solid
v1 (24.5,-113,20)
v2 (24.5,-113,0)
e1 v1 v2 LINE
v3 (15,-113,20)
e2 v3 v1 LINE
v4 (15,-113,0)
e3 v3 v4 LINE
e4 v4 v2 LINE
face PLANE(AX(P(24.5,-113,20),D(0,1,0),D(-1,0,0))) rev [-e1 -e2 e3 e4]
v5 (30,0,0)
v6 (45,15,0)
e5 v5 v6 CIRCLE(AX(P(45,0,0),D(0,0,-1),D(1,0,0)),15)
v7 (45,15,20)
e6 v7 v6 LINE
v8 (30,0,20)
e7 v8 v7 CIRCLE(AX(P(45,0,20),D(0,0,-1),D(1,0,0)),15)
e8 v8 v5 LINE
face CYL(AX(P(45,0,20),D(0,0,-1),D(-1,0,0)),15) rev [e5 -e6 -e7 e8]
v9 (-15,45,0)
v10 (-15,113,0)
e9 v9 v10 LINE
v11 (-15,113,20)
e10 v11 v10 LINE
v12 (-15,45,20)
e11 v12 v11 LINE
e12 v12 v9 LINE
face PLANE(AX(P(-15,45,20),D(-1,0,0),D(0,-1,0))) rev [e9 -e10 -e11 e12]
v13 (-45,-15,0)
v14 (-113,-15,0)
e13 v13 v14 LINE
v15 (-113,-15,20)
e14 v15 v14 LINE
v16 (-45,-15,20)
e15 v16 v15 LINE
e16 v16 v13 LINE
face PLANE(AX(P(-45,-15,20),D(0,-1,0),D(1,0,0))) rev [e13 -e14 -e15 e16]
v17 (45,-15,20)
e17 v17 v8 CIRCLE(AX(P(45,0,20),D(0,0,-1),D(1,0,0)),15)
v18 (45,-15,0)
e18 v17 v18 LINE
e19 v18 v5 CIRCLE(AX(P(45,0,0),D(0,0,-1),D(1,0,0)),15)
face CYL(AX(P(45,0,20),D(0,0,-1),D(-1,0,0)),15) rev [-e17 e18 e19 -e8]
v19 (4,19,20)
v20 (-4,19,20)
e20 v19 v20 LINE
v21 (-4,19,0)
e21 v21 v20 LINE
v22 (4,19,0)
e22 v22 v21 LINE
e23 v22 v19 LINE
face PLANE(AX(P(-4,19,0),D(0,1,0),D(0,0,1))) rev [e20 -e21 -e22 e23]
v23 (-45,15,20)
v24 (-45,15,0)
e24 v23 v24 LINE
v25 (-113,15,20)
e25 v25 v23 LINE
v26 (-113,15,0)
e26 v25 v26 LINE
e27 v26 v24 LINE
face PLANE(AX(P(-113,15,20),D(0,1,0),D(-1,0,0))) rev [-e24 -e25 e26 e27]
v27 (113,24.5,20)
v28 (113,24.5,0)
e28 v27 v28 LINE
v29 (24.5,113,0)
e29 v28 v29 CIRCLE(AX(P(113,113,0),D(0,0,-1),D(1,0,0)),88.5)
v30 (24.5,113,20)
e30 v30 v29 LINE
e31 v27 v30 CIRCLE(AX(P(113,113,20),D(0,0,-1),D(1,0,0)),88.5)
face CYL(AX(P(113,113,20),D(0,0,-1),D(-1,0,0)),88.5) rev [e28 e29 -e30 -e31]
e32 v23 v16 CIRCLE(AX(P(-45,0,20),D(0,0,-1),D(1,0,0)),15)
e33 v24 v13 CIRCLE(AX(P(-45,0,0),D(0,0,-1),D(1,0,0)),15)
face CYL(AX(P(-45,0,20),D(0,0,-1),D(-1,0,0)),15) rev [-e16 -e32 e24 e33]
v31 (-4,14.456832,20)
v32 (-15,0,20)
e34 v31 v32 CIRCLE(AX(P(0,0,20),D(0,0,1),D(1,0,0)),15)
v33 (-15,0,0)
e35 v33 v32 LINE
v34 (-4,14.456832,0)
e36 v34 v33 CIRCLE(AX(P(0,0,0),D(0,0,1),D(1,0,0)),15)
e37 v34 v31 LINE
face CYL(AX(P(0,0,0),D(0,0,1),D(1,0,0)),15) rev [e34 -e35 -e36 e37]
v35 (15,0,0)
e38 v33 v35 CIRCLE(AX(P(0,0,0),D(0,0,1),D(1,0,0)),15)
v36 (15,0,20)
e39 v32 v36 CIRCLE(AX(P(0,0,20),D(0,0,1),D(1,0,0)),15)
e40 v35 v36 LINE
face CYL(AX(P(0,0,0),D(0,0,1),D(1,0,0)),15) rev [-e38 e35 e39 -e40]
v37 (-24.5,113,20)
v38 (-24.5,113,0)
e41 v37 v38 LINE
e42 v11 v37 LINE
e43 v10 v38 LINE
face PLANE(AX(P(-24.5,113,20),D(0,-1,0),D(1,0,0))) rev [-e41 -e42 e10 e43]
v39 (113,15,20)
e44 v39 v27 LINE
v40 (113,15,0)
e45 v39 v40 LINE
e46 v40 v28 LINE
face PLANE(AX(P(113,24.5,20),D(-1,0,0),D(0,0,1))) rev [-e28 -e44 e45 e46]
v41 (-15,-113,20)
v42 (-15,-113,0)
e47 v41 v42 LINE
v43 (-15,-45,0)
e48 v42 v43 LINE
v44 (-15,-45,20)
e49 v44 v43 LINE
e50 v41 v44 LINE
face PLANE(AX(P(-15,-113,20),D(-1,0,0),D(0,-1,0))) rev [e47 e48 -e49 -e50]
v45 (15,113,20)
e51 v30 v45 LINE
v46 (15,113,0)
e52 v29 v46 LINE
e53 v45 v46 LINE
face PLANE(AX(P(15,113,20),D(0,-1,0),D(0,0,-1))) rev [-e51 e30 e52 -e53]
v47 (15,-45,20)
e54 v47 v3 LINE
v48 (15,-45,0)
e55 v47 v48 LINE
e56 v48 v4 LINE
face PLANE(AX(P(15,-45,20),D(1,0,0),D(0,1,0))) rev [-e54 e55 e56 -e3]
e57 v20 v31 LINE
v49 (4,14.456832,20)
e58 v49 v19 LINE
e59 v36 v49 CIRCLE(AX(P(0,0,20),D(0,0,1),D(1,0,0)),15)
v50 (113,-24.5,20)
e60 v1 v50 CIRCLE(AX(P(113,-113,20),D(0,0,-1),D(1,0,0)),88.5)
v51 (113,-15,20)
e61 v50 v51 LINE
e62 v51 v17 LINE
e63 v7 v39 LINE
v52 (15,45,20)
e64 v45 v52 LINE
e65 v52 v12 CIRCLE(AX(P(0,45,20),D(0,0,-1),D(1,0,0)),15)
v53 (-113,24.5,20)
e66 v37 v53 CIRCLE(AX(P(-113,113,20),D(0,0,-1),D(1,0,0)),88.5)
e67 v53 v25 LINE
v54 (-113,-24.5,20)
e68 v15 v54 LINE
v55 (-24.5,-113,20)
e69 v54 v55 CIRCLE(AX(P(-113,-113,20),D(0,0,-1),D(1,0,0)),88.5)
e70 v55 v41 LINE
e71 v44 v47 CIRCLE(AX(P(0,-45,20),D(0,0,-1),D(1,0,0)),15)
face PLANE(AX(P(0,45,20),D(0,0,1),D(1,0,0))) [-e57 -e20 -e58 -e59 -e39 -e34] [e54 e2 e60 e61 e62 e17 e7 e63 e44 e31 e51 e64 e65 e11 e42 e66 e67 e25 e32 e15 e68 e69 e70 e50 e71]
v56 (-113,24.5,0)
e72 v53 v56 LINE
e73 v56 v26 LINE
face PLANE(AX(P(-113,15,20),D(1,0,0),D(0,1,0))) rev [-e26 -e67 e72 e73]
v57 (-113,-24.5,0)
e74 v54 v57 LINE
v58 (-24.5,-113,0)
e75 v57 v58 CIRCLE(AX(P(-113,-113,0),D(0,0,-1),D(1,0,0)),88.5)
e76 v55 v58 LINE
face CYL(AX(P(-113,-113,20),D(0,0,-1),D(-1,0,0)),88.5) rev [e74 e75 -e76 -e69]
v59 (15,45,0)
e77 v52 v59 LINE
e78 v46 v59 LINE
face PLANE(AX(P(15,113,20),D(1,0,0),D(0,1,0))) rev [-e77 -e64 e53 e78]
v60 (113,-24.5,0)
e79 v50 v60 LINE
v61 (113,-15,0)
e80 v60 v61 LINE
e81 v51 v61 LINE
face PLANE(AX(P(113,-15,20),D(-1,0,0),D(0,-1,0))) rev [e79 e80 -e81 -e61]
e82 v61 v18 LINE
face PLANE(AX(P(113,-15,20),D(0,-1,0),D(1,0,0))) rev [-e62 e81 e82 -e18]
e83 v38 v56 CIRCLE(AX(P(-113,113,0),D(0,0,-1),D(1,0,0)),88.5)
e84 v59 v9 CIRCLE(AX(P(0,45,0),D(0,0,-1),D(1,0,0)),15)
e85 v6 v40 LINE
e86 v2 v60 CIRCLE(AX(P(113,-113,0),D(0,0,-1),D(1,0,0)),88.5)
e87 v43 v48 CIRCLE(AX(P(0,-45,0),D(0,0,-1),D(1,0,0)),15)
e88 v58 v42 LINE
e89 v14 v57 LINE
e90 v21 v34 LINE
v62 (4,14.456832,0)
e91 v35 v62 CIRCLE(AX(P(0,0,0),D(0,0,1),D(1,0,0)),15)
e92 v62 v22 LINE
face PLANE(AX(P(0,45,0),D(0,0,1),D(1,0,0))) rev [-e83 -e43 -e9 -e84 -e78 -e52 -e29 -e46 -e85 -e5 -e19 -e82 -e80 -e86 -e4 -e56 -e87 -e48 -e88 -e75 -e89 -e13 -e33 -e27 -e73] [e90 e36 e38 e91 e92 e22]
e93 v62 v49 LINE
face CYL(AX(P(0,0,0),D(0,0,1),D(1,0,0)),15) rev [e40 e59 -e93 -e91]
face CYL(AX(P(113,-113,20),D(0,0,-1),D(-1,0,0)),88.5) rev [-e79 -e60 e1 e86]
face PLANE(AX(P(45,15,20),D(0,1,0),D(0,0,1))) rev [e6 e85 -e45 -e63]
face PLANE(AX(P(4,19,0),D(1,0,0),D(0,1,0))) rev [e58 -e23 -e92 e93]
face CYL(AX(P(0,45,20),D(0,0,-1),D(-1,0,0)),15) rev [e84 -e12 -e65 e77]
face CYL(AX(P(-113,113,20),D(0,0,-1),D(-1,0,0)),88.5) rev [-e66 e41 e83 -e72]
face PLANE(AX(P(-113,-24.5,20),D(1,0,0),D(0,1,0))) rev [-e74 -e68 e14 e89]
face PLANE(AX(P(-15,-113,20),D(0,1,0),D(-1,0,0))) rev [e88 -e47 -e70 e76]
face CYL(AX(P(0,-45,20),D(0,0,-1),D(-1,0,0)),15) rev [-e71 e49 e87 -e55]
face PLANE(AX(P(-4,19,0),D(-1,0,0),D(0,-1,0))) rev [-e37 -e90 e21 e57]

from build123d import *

# Parameters (mm, degrees)
EXTRUDE_1_DEPTH     = 20
CUT_EXTRUDE_1_DEPTH = 162.052786378


with BuildPart() as part:
    # 草图1 → 凸台-拉伸1 (new body)
    with BuildSketch(Plane.XY):
        with BuildLine():
            Line((45, 15), (113, 15))
            Line((113, 15), (113, 24.5))
            ThreePointArc((113, 24.5), (50.421049865, 50.421049865), (24.5, 113))
            Line((24.5, 113), (15, 113))
            Line((15, 113), (15, 45))
            ThreePointArc((15, 45), (10.606601718, 34.393398282), (0, 30))
            ThreePointArc((0, 30), (-10.606601718, 34.393398282), (-15, 45))
            Line((-15, 45), (-15, 113))
            Line((-15, 113), (-24.5, 113))
            ThreePointArc((-24.5, 113), (-50.421049865, 50.421049865), (-113, 24.5))
            Line((-113, 24.5), (-113, 15))
            Line((-113, 15), (-45, 15))
            ThreePointArc((-45, 15), (-34.393398282, 10.606601718), (-30, 0))
            ThreePointArc((-30, 0), (-34.393398282, -10.606601718), (-45, -15))
            Line((-45, -15), (-113, -15))
            Line((-113, -15), (-113, -24.5))
            ThreePointArc((-113, -24.5), (-50.421049865, -50.421049865), (-24.5, -113))
            Line((-24.5, -113), (-15, -113))
            Line((-15, -113), (-15, -45))
            ThreePointArc((-15, -45), (-10.606601718, -34.393398282), (0, -30))
            ThreePointArc((0, -30), (10.606601718, -34.393398282), (15, -45))
            Line((15, -45), (15, -113))
            Line((15, -113), (24.5, -113))
            ThreePointArc((24.5, -113), (50.421049865, -50.421049865), (113, -24.5))
            Line((113, -24.5), (113, -15))
            Line((113, -15), (45, -15))
            ThreePointArc((45, -15), (34.393398282, -10.606601718), (30, 0))
            ThreePointArc((30, 0), (34.393398282, 10.606601718), (45, 15))
        make_face()
    extrude(amount=EXTRUDE_1_DEPTH)

    # 草图2 → 切除-拉伸1 (cut, through all)
    with BuildSketch(Plane.XY.offset(20)):
        with BuildLine():
            Line((-4, 19), (4, 19))
            Line((4, 19), (4, 14.456832295))
            ThreePointArc((4, 14.456832295), (0, -15), (-4, 14.456832295))
            Line((-4, 14.456832295), (-4, 19))
        make_face()
    extrude(amount=-CUT_EXTRUDE_1_DEPTH, mode=Mode.SUBTRACT)


solid = part.part
